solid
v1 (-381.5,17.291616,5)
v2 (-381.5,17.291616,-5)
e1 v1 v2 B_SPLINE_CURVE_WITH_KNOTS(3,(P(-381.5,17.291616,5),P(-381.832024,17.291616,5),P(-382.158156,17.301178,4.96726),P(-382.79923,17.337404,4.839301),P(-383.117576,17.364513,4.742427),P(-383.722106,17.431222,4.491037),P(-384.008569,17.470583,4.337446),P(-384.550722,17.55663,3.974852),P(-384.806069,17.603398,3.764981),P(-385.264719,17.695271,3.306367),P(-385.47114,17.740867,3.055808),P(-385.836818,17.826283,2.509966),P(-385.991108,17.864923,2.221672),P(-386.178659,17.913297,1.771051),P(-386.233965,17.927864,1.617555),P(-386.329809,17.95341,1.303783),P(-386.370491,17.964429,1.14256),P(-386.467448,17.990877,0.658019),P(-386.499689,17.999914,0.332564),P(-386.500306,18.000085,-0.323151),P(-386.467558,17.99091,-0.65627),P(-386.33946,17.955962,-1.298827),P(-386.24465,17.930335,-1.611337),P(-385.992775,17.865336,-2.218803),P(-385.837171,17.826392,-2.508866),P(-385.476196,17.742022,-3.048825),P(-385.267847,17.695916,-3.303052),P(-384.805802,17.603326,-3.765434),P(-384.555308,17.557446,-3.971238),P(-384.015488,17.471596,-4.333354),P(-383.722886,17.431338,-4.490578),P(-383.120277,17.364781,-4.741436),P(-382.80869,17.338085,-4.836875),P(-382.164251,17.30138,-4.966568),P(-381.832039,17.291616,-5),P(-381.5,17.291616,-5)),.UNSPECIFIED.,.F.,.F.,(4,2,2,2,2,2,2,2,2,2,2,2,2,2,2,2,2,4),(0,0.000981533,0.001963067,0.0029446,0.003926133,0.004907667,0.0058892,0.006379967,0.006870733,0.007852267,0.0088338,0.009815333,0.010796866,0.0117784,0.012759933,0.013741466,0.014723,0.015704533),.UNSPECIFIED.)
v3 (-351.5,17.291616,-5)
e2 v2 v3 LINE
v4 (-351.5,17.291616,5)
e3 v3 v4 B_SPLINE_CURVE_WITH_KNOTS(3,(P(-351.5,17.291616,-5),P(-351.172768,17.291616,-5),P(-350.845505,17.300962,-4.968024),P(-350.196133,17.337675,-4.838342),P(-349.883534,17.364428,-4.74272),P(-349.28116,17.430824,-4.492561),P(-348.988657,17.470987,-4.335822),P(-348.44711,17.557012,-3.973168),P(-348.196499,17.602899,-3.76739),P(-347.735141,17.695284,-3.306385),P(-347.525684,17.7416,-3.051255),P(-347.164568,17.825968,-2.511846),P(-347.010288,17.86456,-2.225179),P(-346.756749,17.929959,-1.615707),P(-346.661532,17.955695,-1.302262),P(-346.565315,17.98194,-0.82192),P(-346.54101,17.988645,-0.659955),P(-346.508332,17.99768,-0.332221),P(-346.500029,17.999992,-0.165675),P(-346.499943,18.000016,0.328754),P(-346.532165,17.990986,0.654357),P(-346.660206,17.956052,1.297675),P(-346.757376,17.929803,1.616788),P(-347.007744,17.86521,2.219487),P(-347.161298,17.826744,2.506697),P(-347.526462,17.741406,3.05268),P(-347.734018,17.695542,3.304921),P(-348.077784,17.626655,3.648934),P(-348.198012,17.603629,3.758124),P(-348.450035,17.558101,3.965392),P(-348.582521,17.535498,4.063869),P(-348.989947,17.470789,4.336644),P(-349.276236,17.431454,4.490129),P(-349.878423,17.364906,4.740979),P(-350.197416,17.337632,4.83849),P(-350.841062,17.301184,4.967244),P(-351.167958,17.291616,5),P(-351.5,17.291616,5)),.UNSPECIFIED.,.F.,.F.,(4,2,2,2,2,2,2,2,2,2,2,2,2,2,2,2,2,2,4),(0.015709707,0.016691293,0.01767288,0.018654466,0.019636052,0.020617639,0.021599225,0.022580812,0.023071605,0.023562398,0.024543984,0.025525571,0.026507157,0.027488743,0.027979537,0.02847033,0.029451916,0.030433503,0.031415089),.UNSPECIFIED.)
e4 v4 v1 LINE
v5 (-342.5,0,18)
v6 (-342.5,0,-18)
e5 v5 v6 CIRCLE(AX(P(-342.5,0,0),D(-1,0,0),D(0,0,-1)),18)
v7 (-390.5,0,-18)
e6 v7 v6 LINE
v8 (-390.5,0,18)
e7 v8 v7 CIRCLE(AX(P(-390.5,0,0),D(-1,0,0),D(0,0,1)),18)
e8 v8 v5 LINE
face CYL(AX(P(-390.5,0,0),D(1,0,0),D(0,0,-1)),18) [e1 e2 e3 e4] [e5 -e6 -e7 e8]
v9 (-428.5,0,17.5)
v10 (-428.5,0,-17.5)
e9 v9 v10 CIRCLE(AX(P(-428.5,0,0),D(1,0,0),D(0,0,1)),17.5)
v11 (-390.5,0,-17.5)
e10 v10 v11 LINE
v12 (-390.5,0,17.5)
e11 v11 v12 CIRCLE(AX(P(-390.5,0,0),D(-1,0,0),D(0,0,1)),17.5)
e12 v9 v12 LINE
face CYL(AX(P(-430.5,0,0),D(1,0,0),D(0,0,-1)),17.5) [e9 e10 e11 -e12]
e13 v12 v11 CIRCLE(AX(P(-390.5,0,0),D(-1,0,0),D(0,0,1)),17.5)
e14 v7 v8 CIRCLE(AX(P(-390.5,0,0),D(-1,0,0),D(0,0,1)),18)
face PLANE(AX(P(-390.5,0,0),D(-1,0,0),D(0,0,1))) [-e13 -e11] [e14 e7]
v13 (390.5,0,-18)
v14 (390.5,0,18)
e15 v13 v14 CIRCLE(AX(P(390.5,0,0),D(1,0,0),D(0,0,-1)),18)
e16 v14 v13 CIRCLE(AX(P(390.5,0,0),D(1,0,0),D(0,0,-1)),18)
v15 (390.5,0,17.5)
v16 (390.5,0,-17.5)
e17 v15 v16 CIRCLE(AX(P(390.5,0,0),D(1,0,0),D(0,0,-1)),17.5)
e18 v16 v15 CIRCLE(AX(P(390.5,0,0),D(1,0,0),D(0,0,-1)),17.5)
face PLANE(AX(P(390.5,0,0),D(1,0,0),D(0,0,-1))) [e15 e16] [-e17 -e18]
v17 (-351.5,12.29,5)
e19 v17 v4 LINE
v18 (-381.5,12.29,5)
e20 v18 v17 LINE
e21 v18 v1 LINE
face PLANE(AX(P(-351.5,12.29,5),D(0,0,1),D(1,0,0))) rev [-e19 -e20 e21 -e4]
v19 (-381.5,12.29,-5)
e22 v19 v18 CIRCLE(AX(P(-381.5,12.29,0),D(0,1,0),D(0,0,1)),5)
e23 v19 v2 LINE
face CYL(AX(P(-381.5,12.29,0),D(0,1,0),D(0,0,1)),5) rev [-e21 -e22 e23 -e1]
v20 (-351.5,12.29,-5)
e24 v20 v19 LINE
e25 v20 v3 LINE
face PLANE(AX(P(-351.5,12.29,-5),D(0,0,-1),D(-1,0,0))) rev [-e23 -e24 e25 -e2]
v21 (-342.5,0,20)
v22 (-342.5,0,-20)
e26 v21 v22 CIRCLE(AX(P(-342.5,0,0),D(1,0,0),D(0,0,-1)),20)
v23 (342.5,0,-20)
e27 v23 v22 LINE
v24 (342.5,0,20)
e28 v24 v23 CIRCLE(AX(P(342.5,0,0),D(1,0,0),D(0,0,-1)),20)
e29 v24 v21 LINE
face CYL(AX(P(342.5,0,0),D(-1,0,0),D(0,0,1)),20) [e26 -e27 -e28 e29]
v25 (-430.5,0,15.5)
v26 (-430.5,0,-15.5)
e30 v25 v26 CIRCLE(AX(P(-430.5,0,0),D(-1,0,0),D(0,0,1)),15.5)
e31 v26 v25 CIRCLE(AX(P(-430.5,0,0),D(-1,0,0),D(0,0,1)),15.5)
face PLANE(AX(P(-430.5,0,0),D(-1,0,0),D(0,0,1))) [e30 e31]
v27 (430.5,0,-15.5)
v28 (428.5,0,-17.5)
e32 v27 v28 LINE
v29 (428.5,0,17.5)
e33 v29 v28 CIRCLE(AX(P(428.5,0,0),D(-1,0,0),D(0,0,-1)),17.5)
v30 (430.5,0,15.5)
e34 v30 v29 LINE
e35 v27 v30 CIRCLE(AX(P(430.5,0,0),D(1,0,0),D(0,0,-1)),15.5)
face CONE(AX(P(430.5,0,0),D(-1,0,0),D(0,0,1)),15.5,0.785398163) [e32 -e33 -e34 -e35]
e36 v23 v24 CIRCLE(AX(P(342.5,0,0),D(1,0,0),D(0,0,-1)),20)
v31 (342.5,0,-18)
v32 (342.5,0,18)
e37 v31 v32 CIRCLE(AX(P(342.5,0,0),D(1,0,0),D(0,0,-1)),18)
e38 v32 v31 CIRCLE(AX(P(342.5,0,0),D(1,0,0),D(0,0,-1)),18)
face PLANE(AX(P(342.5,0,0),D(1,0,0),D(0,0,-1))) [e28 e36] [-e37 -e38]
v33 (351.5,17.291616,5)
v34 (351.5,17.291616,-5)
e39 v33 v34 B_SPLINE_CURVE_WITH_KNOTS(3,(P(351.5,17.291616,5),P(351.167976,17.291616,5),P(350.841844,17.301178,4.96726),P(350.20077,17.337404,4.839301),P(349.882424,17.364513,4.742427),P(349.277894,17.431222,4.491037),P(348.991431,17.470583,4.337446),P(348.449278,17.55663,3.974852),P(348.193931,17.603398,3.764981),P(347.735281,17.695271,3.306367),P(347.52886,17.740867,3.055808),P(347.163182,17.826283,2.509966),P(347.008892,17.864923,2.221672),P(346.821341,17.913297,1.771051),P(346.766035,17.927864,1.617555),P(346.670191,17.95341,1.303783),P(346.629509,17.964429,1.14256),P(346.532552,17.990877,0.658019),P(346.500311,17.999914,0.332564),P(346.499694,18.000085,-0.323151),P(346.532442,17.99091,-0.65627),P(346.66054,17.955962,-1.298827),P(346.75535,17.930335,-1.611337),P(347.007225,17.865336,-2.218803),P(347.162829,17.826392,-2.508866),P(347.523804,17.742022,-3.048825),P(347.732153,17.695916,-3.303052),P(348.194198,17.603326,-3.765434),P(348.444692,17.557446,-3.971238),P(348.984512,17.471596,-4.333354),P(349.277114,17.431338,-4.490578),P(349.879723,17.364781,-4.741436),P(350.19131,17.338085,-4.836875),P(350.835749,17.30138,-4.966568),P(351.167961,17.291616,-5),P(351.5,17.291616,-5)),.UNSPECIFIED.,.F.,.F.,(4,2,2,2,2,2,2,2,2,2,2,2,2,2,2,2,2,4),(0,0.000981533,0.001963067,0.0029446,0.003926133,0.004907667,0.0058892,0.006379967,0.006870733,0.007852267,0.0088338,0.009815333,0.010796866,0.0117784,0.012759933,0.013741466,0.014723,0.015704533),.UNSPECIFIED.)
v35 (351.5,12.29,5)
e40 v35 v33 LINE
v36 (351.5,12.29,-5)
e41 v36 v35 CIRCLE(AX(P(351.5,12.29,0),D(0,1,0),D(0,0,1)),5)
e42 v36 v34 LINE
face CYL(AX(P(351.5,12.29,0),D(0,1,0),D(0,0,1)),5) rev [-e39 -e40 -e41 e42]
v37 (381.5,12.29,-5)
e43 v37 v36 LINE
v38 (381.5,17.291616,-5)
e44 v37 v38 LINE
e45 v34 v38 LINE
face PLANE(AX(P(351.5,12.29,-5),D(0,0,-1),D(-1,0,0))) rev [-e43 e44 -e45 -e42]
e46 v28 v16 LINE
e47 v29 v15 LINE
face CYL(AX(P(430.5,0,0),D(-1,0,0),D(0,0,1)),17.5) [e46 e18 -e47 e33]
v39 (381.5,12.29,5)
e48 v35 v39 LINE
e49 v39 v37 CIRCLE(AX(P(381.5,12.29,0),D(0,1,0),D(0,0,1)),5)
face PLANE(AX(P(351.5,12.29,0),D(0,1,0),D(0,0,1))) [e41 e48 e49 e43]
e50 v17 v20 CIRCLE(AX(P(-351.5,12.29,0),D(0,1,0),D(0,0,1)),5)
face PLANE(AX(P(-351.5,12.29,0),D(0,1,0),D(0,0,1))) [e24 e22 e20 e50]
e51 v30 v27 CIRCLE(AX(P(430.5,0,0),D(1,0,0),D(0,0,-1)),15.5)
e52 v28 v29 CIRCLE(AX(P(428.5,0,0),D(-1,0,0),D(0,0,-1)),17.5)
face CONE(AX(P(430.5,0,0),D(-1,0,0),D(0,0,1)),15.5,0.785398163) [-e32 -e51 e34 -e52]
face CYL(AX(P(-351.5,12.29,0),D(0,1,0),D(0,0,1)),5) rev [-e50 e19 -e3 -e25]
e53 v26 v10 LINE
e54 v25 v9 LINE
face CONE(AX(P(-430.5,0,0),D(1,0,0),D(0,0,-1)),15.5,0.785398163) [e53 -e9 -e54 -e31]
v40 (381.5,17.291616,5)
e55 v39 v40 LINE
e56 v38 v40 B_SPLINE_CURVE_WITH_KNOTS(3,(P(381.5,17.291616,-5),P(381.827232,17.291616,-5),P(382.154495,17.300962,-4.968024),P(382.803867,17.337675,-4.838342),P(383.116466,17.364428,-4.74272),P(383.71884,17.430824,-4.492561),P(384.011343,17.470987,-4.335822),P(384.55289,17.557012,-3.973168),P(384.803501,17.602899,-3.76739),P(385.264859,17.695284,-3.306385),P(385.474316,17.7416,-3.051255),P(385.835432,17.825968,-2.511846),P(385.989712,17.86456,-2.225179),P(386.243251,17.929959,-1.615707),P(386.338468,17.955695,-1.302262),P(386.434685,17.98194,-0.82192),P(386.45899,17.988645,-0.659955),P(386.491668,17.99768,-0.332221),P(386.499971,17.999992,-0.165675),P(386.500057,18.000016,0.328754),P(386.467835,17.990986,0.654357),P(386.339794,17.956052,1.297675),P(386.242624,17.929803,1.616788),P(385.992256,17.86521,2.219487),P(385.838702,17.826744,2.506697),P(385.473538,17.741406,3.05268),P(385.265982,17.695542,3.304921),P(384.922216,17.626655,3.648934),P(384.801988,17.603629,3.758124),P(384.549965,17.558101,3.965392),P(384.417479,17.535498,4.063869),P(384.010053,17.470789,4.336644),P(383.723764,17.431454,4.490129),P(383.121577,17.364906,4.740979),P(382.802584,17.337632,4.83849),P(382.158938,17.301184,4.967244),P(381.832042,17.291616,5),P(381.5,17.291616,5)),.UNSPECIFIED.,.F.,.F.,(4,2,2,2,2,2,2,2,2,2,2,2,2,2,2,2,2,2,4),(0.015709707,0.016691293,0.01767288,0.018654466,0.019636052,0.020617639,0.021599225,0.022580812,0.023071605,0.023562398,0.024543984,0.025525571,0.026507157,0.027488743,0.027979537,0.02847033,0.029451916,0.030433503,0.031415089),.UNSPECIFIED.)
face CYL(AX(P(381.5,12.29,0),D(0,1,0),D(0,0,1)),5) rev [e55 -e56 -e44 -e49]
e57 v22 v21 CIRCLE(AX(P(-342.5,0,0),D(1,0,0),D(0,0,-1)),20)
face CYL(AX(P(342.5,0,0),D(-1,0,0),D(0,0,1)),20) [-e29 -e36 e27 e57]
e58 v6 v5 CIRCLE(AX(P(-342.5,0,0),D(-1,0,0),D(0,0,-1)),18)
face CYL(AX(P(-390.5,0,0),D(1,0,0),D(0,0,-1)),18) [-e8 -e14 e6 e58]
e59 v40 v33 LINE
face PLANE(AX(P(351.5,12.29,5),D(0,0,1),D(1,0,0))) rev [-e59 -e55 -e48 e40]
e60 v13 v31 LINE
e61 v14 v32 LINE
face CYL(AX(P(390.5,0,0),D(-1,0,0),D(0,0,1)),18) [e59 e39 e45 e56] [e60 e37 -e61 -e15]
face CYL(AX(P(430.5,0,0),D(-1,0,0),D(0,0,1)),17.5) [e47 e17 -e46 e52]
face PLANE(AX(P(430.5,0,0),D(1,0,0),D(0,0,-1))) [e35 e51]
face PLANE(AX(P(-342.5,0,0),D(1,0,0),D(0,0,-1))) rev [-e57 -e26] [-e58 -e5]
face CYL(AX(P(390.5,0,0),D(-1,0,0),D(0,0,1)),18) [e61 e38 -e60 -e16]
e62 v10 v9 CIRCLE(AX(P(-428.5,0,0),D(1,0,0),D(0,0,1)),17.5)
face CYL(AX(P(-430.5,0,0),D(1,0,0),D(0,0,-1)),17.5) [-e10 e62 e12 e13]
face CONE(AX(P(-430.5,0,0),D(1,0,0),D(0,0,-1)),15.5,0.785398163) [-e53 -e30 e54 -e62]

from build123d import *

# Parameters (mm, degrees)
SKETCH_1_R          = 20
EXTRUDE_1_DEPTH     = 342.5
SKETCH_2_R          = 18
EXTRUDE_2_DEPTH     = 48
SKETCH_3_R          = 17.5
EXTRUDE_3_DEPTH     = 40
EXTRUDE_START       = 48
SKETCH_4_R          = 18
EXTRUDE_4_DEPTH     = 48
EXTRUDE_START_2     = 40
SKETCH_5_R          = 17.5
EXTRUDE_5_DEPTH     = 40
CUT_EXTRUDE_1_DEPTH = 5.71
CHAMFER_1_SIZE      = 2


with BuildPart() as part:
    # 草图1 → 凸台-拉伸1 (new, symmetric)
    with BuildSketch(Plane(origin=(0, 0, 0), x_dir=(0, 0, -1), z_dir=(1, 0, 0))):
        Circle(SKETCH_1_R)
    extrude(amount=EXTRUDE_1_DEPTH, both=True)

    # 草图2 → 凸台-拉伸2 (add)
    with BuildSketch(Plane.ZY.offset(342.5)):
        with Locations(Location((0, 0, 0), (0, 0, 180))):
            Circle(SKETCH_2_R)
    extrude(amount=EXTRUDE_2_DEPTH)

    # 草图3 → 凸台-拉伸3 (add)
    with BuildSketch(Plane.ZY.offset(390.5)):
        Circle(SKETCH_3_R)
    extrude(amount=EXTRUDE_3_DEPTH)

    # 草图4 → 凸台-拉伸4 (add)
    with BuildSketch(Plane(origin=(342.5, 0, 0), x_dir=(0, 0, -1), z_dir=(1, 0, 0)).offset(EXTRUDE_START)):
        Circle(SKETCH_4_R)
    extrude(amount=-EXTRUDE_4_DEPTH)

    # 草图5 → 凸台-拉伸5 (add)
    with BuildSketch(Plane(origin=(390.5, 0, 0), x_dir=(0, 0, -1), z_dir=(1, 0, 0)).offset(EXTRUDE_START_2)):
        with Locations(Location((0, 0, 0), (0, 0, 180))):
            Circle(SKETCH_5_R)
    extrude(amount=-EXTRUDE_5_DEPTH)

    # 草图7 → 切除-拉伸1 (cut)
    with BuildSketch(Plane(origin=(0, 18, 0), x_dir=(1, 0, 0), z_dir=(0, 1, 0))):
        with BuildLine():
            Line((351.5, 5), (381.5, 5))
            ThreePointArc((381.5, 5), (386.5, 0), (381.5, -5))
            Line((381.5, -5), (351.5, -5))
            ThreePointArc((351.5, -5), (346.5, 0), (351.5, 5))
        make_face()
        with BuildLine():
            Line((-351.5, -5), (-381.5, -5))
            ThreePointArc((-381.5, -5), (-386.5, 0), (-381.5, 5))
            Line((-381.5, 5), (-351.5, 5))
            ThreePointArc((-351.5, 5), (-346.5, 0), (-351.5, -5))
        make_face()
    extrude(amount=-CUT_EXTRUDE_1_DEPTH, mode=Mode.SUBTRACT)

    # 倒角1
    chamfer_1_edges = [part.edges().sort_by_distance(p)[0] for p in [
        (-430.5, 0, -17.5),
        (430.5, 0, -17.5),
    ]]
    chamfer(chamfer_1_edges, length=CHAMFER_1_SIZE)


solid = part.part
